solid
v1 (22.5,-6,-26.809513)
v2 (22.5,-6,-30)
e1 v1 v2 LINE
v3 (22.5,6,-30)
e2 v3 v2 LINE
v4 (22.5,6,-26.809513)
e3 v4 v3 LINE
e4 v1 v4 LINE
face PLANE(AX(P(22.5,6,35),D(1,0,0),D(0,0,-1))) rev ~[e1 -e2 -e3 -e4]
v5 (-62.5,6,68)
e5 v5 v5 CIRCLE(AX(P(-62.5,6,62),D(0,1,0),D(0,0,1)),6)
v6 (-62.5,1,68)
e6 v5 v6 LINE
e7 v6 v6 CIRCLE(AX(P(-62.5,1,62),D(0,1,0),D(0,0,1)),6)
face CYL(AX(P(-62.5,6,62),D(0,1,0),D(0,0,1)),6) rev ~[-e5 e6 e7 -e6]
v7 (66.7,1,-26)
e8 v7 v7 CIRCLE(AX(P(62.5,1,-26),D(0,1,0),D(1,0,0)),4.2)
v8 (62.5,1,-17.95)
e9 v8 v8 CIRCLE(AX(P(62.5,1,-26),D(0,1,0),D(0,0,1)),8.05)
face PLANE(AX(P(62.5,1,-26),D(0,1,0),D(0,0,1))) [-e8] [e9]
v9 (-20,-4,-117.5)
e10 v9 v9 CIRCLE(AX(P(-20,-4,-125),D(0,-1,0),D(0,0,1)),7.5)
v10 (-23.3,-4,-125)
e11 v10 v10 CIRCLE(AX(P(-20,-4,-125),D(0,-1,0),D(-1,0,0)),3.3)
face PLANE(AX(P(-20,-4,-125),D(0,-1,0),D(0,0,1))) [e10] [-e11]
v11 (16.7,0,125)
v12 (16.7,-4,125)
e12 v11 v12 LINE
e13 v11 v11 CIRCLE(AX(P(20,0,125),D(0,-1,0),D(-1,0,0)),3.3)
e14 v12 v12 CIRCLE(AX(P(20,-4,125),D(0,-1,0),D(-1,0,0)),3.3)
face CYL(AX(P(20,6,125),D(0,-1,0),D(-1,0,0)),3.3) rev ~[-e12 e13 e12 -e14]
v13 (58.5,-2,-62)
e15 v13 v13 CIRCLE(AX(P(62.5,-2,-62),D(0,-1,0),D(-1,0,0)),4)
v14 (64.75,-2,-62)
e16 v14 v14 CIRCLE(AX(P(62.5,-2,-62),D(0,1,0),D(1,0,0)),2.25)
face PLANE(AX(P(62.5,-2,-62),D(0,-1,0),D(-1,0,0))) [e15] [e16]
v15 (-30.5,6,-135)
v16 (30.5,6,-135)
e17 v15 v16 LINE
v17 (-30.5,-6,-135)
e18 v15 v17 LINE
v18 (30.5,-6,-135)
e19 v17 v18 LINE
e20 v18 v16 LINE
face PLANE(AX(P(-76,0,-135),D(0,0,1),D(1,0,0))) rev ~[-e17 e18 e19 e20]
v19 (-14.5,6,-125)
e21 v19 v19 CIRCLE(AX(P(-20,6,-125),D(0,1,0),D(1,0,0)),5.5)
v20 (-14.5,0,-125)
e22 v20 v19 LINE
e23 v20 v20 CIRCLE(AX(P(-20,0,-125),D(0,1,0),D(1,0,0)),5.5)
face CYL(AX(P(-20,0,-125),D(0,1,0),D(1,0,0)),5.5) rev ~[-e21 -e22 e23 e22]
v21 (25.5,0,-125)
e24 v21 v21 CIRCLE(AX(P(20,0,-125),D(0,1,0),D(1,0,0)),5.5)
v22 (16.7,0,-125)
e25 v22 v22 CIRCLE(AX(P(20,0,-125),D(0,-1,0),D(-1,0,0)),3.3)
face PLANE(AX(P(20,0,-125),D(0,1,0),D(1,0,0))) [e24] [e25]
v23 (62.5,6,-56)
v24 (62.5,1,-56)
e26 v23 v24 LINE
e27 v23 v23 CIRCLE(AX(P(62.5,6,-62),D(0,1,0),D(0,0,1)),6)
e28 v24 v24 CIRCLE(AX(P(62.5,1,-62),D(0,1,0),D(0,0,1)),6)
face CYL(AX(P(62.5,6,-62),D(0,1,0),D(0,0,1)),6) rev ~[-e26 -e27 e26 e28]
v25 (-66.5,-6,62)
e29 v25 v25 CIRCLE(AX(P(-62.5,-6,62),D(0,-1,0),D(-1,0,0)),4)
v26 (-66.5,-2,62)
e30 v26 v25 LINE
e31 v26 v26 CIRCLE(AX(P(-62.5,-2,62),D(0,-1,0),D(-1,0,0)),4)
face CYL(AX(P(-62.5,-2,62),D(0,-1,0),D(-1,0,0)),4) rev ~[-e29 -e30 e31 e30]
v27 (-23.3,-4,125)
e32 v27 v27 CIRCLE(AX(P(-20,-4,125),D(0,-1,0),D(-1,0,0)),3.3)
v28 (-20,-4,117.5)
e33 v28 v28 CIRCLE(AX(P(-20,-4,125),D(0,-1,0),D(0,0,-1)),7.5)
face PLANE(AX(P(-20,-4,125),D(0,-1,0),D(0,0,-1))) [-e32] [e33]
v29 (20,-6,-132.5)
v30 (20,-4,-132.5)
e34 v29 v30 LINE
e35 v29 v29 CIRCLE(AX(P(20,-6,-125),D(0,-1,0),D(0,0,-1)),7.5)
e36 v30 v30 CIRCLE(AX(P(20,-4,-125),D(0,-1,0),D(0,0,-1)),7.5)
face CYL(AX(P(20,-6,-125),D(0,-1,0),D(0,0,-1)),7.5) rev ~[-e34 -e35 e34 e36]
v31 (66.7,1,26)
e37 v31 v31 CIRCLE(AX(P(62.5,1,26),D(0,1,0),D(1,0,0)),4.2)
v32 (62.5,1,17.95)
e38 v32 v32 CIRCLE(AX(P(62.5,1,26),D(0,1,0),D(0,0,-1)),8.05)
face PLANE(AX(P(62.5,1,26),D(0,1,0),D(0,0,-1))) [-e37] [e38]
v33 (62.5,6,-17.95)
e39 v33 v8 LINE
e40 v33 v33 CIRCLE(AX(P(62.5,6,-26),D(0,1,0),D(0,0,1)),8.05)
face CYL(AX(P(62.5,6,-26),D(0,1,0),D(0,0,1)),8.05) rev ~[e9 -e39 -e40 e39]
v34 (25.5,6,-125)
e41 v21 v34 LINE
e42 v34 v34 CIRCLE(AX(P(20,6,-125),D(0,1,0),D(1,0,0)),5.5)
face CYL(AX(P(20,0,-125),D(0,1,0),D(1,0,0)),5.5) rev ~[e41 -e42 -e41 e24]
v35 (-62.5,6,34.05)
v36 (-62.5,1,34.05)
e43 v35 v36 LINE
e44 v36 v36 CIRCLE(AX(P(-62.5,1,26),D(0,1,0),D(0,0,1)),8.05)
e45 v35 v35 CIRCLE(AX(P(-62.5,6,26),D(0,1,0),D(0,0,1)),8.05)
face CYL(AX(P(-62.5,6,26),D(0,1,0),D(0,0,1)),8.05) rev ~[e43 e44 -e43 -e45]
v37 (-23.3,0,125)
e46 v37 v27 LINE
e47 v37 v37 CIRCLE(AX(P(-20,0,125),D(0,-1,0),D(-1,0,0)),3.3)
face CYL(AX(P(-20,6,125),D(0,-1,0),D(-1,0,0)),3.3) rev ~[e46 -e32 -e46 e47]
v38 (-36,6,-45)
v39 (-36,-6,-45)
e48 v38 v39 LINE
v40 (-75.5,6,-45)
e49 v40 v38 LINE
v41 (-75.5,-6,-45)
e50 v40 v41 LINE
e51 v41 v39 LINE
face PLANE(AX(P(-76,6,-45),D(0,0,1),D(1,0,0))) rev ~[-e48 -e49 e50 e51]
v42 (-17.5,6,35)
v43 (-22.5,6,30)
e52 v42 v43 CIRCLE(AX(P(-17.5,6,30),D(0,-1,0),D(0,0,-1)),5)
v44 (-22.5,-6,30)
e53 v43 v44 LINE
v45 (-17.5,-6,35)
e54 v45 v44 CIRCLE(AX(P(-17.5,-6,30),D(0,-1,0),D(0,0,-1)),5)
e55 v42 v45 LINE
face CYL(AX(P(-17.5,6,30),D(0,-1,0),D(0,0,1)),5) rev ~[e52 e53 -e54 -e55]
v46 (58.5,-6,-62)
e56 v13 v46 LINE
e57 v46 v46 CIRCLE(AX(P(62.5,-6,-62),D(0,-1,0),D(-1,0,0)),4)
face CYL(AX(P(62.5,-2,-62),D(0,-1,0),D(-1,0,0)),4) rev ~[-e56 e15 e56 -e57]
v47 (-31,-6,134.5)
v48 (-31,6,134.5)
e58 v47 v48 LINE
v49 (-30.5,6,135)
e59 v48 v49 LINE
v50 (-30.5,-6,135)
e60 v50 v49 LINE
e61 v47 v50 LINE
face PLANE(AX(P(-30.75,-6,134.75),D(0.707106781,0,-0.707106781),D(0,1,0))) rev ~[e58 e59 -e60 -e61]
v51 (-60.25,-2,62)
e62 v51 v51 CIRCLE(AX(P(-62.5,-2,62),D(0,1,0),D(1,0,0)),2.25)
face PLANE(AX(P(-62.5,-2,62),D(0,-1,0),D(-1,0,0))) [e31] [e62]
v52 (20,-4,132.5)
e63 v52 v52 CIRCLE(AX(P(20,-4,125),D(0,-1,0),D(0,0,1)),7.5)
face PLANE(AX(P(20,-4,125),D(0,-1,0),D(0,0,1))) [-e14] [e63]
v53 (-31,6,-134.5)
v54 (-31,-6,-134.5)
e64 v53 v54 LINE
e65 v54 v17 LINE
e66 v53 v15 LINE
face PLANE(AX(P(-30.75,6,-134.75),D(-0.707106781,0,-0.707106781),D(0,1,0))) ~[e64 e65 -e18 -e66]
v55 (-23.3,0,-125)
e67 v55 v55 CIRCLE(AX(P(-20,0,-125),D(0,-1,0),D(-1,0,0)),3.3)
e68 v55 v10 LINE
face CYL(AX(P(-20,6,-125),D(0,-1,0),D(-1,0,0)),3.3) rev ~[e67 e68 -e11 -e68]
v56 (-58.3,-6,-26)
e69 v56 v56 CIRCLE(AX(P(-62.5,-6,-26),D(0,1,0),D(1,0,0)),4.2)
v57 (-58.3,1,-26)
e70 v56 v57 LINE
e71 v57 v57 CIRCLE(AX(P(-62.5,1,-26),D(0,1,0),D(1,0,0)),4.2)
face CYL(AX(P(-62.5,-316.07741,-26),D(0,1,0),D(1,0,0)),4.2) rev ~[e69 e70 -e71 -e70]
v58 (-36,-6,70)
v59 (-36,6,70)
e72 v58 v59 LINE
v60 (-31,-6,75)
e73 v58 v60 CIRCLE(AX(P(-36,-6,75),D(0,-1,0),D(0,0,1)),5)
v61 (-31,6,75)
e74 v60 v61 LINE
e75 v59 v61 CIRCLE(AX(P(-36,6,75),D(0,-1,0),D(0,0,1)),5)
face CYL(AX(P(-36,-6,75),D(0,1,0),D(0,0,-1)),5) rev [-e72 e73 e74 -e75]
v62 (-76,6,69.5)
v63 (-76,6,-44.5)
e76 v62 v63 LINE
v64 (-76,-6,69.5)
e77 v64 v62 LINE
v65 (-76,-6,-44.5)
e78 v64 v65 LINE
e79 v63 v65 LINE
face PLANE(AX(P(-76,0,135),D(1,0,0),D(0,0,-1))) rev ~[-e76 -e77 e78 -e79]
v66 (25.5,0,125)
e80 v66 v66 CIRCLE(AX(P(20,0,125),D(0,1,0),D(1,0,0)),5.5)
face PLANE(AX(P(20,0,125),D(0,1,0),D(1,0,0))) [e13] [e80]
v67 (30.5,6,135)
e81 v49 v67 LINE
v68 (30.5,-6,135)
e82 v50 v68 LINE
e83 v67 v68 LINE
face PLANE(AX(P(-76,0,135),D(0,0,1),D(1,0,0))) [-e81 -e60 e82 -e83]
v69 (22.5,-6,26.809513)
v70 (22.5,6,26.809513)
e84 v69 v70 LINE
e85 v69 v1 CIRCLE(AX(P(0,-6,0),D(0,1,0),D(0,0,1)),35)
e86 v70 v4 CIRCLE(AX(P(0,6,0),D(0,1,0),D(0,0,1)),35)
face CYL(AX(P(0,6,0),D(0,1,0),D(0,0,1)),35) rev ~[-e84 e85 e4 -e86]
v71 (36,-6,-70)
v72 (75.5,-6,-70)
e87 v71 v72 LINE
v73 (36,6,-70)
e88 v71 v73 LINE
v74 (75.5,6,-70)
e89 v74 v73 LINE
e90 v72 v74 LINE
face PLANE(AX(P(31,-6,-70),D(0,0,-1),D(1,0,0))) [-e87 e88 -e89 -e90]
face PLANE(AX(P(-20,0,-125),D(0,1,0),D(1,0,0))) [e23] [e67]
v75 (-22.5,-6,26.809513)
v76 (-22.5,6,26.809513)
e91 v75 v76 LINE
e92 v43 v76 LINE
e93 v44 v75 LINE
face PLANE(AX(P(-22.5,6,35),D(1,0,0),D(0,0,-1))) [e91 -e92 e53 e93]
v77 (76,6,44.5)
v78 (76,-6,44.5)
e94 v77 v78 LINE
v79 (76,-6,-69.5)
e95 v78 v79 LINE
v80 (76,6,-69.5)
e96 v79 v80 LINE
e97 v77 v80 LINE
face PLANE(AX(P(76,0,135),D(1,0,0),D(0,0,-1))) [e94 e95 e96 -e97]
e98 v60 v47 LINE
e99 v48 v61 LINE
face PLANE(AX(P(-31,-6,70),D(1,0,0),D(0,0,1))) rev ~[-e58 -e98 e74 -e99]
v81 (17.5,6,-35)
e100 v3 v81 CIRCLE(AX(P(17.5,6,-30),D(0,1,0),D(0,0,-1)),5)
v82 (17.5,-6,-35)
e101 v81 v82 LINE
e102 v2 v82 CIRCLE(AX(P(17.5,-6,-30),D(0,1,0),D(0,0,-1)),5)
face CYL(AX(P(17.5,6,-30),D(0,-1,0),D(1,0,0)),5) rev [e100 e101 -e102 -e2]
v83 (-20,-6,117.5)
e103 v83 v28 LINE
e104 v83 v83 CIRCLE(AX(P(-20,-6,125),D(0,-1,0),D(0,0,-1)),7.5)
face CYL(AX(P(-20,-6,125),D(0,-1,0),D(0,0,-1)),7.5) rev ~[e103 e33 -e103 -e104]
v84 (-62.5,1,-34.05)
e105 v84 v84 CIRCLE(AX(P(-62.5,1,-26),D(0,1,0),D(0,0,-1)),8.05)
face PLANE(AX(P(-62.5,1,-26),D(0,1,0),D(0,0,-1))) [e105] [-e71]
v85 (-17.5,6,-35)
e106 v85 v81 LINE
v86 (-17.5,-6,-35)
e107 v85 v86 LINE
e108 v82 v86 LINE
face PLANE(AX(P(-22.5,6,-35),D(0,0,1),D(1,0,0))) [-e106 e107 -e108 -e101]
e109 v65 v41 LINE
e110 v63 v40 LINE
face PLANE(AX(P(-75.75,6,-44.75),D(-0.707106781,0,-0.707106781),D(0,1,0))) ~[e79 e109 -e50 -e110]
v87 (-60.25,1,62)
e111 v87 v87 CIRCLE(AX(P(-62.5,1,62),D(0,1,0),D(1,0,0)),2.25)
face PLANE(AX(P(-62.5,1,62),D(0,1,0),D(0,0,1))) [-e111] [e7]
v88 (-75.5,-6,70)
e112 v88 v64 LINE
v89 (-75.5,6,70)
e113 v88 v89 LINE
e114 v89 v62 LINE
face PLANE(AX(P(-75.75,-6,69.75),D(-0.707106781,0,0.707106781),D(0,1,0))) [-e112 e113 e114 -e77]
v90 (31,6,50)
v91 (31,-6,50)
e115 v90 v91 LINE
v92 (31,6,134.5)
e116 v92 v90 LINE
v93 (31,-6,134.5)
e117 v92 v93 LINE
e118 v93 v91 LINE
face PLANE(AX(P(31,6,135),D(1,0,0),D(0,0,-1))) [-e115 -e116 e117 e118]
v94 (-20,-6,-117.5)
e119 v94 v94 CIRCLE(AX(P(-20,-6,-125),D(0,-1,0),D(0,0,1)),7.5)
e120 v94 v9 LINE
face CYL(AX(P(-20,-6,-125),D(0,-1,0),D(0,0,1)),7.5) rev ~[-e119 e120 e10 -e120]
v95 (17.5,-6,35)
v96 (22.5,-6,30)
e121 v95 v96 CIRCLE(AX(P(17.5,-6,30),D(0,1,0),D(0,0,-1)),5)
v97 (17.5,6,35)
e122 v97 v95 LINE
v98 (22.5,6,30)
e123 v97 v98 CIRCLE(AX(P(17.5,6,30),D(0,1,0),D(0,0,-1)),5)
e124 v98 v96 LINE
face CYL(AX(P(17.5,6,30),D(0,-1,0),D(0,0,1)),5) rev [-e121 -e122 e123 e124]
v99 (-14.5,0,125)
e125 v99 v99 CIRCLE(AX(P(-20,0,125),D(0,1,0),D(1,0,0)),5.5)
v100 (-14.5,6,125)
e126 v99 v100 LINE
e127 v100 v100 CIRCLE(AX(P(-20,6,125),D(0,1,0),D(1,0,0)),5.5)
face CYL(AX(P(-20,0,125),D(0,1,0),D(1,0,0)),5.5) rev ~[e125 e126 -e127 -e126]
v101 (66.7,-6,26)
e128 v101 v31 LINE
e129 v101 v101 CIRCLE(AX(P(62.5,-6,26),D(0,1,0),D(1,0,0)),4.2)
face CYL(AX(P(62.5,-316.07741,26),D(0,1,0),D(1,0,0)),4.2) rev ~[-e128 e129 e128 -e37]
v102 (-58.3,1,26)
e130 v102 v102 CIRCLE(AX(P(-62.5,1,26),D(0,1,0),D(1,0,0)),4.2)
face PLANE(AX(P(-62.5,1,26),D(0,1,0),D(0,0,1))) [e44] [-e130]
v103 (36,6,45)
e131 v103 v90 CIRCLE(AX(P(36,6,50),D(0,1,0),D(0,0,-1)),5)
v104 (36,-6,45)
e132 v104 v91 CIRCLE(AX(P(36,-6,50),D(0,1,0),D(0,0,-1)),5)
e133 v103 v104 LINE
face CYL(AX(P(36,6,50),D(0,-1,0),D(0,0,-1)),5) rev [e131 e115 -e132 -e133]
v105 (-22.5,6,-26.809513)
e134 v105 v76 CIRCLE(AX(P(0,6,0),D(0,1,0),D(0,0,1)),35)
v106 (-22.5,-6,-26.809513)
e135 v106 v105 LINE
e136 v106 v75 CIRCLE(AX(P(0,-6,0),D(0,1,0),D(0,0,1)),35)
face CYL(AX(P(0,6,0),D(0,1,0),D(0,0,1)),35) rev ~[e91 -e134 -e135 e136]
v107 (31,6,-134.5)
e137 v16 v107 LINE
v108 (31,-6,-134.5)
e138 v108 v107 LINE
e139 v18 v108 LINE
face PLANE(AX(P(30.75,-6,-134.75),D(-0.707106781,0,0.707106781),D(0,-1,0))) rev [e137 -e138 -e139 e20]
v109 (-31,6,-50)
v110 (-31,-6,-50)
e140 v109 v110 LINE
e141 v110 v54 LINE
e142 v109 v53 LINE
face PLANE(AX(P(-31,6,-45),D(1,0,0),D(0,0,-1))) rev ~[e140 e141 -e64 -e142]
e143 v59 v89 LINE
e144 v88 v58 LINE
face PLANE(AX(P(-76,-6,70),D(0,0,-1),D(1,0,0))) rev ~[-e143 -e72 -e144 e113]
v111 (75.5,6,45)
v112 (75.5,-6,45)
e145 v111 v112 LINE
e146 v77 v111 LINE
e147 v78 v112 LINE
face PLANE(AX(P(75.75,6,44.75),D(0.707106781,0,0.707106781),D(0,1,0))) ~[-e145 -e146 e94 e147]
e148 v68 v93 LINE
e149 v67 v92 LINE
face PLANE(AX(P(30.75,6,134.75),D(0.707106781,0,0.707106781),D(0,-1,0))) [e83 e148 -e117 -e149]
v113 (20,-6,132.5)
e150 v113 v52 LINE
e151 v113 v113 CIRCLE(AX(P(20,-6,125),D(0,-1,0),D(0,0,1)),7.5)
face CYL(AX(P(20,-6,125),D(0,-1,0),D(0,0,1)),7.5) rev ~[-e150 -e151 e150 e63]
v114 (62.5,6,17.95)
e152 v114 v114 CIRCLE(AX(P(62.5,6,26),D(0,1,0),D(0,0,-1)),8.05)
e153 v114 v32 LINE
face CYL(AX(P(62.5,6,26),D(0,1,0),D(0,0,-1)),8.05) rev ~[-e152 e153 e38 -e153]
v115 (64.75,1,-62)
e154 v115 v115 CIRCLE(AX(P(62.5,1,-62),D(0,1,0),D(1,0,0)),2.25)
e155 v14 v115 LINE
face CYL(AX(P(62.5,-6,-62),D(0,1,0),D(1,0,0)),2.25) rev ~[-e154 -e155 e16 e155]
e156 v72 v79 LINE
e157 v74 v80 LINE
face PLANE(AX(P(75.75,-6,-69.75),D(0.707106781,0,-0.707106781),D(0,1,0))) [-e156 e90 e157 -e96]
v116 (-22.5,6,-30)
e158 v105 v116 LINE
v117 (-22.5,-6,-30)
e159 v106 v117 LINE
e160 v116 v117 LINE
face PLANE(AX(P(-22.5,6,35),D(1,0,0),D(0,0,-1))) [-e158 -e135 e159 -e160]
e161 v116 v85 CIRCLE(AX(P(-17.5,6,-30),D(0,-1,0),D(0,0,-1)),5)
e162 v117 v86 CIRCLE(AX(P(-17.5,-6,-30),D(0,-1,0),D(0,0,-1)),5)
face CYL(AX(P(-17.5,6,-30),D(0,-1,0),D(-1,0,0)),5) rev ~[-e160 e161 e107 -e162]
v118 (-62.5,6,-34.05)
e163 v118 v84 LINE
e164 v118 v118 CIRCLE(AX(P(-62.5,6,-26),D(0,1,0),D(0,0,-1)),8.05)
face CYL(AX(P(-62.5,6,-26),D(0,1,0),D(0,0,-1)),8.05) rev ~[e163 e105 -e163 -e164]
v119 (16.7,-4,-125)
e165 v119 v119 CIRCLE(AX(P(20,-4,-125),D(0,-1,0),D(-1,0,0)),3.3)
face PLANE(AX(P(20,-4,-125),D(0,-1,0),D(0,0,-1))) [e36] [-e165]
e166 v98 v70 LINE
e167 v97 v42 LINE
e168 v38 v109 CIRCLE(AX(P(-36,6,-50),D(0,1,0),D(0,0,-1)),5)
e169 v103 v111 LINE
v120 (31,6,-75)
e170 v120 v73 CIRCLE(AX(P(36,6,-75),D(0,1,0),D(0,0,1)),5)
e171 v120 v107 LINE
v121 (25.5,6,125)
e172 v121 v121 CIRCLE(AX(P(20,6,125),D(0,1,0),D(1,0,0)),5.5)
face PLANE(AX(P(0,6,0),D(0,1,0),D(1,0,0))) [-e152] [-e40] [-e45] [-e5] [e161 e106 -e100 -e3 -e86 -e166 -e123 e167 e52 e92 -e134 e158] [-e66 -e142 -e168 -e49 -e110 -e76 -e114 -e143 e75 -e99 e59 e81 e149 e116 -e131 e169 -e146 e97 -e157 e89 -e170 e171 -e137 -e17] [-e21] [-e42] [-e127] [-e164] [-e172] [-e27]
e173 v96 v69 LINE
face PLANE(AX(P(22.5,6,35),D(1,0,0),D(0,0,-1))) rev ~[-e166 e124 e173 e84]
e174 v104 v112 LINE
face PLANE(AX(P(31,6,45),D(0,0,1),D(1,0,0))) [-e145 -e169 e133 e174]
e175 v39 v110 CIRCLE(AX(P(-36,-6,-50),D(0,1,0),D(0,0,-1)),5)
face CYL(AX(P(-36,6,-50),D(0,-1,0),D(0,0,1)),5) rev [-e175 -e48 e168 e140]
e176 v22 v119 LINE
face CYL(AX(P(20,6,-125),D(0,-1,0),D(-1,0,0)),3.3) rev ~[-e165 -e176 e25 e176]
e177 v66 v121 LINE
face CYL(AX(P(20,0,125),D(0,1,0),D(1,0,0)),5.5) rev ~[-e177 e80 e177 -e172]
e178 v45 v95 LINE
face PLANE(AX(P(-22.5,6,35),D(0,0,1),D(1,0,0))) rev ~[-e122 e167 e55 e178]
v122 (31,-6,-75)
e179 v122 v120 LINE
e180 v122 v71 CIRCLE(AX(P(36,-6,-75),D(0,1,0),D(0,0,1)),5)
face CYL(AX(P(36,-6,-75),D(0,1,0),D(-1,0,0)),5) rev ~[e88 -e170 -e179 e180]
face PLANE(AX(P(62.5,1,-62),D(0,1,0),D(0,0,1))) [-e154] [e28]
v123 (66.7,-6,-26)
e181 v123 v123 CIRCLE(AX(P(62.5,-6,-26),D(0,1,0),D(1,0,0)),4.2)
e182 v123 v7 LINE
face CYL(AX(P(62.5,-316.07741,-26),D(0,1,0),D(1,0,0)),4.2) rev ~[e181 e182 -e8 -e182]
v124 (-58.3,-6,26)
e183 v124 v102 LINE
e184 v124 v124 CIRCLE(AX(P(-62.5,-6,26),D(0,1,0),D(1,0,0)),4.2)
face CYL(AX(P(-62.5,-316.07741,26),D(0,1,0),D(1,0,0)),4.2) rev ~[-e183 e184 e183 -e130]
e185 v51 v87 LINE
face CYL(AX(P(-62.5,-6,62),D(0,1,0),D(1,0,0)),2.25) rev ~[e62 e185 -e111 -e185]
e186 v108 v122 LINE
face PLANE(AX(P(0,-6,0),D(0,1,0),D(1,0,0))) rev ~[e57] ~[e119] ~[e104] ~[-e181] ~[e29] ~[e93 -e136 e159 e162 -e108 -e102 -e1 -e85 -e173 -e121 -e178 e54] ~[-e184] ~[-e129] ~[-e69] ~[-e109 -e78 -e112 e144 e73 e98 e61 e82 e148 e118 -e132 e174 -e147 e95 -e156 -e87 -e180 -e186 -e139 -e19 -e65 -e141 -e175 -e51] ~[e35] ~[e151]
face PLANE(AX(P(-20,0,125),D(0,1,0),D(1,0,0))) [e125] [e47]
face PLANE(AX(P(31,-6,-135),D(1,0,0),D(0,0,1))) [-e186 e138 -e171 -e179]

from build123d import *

# Parameters (mm, degrees)
SKETCH1_W                                            = 152
SKETCH1_H                                            = 270
BOSS_EXTRUDE1_DEPTH                                  = 6
SKETCH2_R                                            = 35
CUT_EXTRUDE1_DEPTH                                   = 156.38661461
SKETCH5_R                                            = 6
SKETCH5_R_2                                          = 8.05
CUT_EXTRUDE2_DEPTH                                   = 5
SKETCH6_W                                            = 45
SKETCH6_H                                            = 70
CUT_EXTRUDE3_DEPTH                                   = 156.38661461
SKETCH7_W                                            = 45
SKETCH7_H                                            = 90
CUT_EXTRUDE4_DEPTH                                   = 156.38661461
SKETCH8_R                                            = 7.5
CUT_EXTRUDE5_DEPTH                                   = 2
SKETCH9_W                                            = 45
SKETCH9_H                                            = 65
CUT_EXTRUDE6_DEPTH                                   = 156.38661461
FILLET1_R                                            = 5
HOLE_SIZE_PER_SOCKET_HEAD_CAP_SCREW_TYPE_D           = 6.6
HOLE_SIZE_PER_SOCKET_HEAD_CAP_SCREW_TYPE_CBORE_D     = 11
HOLE_SIZE_PER_SOCKET_HEAD_CAP_SCREW_TYPE_CBORE_DEPTH = 6
HOLE_WIZARD_2_D                                      = 4.5
HOLE_WIZARD_2_CBORE_D                                = 8
HOLE_WIZARD_2_CBORE_DEPTH                            = 4
M8_CLEARANCE_HOLE1_D                                 = 8.4
CHAMFER1_SIZE                                        = 0.5


with BuildPart() as part:
    # Sketch1 → Boss-Extrude1 (new, symmetric)
    with BuildSketch(Plane(origin=(0, 0, 0), x_dir=(1, 0, 0), z_dir=(0, 1, 0))):
        Rectangle(SKETCH1_W, SKETCH1_H)
    extrude(amount=BOSS_EXTRUDE1_DEPTH, both=True)

    # Sketch2 → Cut-Extrude1 (cut, through all)
    with BuildSketch(Plane(origin=(0, 6, 0), x_dir=(1, 0, 0), z_dir=(0, 1, 0))):
        with Locations(Location((0, 0, 0), (0, 0, 270))):
            Circle(SKETCH2_R)
    extrude(amount=-CUT_EXTRUDE1_DEPTH, mode=Mode.SUBTRACT)

    # Sketch5 → Cut-Extrude2 (cut)
    with BuildSketch(Plane(origin=(0, 6, 0), x_dir=(1, 0, 0), z_dir=(0, 1, 0))):
        with Locations(Location((62.5, 62, 0), (0, 0, 270))):
            Circle(SKETCH5_R)
        with Locations(Location((-62.5, -62, 0), (0, 0, 270))):
            Circle(SKETCH5_R)
        with Locations(Location((62.5, 26, 0), (0, 0, 270))):
            Circle(SKETCH5_R_2)
        with Locations(Location((-62.5, 26, 0), (0, 0, 90))):
            Circle(SKETCH5_R_2)
        with Locations(Location((-62.5, -26, 0), (0, 0, 270))):
            Circle(SKETCH5_R_2)
        with Locations(Location((62.5, -26, 0), (0, 0, 90))):
            Circle(SKETCH5_R_2)
    extrude(amount=-CUT_EXTRUDE2_DEPTH, mode=Mode.SUBTRACT)

    # Sketch6 → Cut-Extrude3 (cut, through all)
    with BuildSketch(Plane(origin=(0, 6, 0), x_dir=(1, 0, 0), z_dir=(0, 1, 0))):
        Rectangle(SKETCH6_W, SKETCH6_H)
    extrude(amount=-CUT_EXTRUDE3_DEPTH, mode=Mode.SUBTRACT)

    # Sketch7 → Cut-Extrude4 (cut, through all)
    with BuildSketch(Plane(origin=(0, 6, 0), x_dir=(1, 0, 0), z_dir=(0, 1, 0))):
        with Locations((-53.5, 90)):
            Rectangle(SKETCH7_W, SKETCH7_H)
        with Locations((53.5, -90)):
            Rectangle(SKETCH7_W, SKETCH7_H)
    extrude(amount=-CUT_EXTRUDE4_DEPTH, mode=Mode.SUBTRACT)

    # Sketch8 → Cut-Extrude5 (cut)
    with BuildSketch(Plane.XZ.offset(6)):
        with Locations(Location((-20, 125, 0), (0, 0, 270))):
            Circle(SKETCH8_R)
        with Locations(Location((20, 125, 0), (0, 0, 90))):
            Circle(SKETCH8_R)
        with Locations(Location((20, -125, 0), (0, 0, 270))):
            Circle(SKETCH8_R)
        with Locations(Location((-20, -125, 0), (0, 0, 90))):
            Circle(SKETCH8_R)
    extrude(amount=-CUT_EXTRUDE5_DEPTH, mode=Mode.SUBTRACT)

    # Sketch9 → Cut-Extrude6 (cut, through all)
    with BuildSketch(Plane.XZ.offset(6)):
        with Locations((-53.5, 102.5)):
            Rectangle(SKETCH9_W, SKETCH9_H)
        with Locations((53.5, -102.5)):
            Rectangle(SKETCH9_W, SKETCH9_H)
    extrude(amount=-CUT_EXTRUDE6_DEPTH, mode=Mode.SUBTRACT)

    # Fillet1
    fillet1_edges = [part.edges().sort_by_distance(p)[0] for p in [
        (-31, 0, 70),
        (31, 0, -70),
        (22.5, 0, -35),
        (22.5, 0, 35),
        (-22.5, 0, 35),
        (-22.5, 0, -35),
        (-31, 0, -45),
        (31, 0, 45),
    ]]
    fillet(fillet1_edges, radius=FILLET1_R)

    # Hole size per socket head cap screw type 2 (through all)
    with Locations(Plane(origin=(0, 6, 0), x_dir=(1, 0, 0), z_dir=(0, 1, 0))):
        with Locations((-20, 125), (20, 125), (-20, -125), (20, -125)):
            CounterBoreHole(HOLE_SIZE_PER_SOCKET_HEAD_CAP_SCREW_TYPE_D / 2, HOLE_SIZE_PER_SOCKET_HEAD_CAP_SCREW_TYPE_CBORE_D / 2, HOLE_SIZE_PER_SOCKET_HEAD_CAP_SCREW_TYPE_CBORE_DEPTH)

    # 打孔尺寸(%根据)内六角圆柱头螺钉的类型2 (through all)
    with Locations(Plane(origin=(0, -6, 0), x_dir=(-1, 0, 0), z_dir=(0, -1, 0))):
        with Locations((62.5, -62), (-62.5, 62)):
            CounterBoreHole(HOLE_WIZARD_2_D / 2, HOLE_WIZARD_2_CBORE_D / 2, HOLE_WIZARD_2_CBORE_DEPTH)

    # M8 Clearance Hole1 (through all)
    with Locations(Plane(origin=(0, -6, 0), x_dir=(-1, 0, 0), z_dir=(0, -1, 0))):
        with Locations((62.5, -26), (62.5, 26), (-62.5, -26), (-62.5, 26)):
            Hole(M8_CLEARANCE_HOLE1_D / 2)

    # Chamfer1
    chamfer1_edges = [part.edges().sort_by_distance(p)[0] for p in [
        (-76, 0, 70),
        (-31, 0, 135),
        (76, 0, -70),
        (31, 0, -135),
        (-76, 0, -45),
        (-31, 0, -135),
        (76, 0, 45),
        (31, 0, 135),
    ]]
    chamfer(chamfer1_edges, length=CHAMFER1_SIZE)


solid = part.part
